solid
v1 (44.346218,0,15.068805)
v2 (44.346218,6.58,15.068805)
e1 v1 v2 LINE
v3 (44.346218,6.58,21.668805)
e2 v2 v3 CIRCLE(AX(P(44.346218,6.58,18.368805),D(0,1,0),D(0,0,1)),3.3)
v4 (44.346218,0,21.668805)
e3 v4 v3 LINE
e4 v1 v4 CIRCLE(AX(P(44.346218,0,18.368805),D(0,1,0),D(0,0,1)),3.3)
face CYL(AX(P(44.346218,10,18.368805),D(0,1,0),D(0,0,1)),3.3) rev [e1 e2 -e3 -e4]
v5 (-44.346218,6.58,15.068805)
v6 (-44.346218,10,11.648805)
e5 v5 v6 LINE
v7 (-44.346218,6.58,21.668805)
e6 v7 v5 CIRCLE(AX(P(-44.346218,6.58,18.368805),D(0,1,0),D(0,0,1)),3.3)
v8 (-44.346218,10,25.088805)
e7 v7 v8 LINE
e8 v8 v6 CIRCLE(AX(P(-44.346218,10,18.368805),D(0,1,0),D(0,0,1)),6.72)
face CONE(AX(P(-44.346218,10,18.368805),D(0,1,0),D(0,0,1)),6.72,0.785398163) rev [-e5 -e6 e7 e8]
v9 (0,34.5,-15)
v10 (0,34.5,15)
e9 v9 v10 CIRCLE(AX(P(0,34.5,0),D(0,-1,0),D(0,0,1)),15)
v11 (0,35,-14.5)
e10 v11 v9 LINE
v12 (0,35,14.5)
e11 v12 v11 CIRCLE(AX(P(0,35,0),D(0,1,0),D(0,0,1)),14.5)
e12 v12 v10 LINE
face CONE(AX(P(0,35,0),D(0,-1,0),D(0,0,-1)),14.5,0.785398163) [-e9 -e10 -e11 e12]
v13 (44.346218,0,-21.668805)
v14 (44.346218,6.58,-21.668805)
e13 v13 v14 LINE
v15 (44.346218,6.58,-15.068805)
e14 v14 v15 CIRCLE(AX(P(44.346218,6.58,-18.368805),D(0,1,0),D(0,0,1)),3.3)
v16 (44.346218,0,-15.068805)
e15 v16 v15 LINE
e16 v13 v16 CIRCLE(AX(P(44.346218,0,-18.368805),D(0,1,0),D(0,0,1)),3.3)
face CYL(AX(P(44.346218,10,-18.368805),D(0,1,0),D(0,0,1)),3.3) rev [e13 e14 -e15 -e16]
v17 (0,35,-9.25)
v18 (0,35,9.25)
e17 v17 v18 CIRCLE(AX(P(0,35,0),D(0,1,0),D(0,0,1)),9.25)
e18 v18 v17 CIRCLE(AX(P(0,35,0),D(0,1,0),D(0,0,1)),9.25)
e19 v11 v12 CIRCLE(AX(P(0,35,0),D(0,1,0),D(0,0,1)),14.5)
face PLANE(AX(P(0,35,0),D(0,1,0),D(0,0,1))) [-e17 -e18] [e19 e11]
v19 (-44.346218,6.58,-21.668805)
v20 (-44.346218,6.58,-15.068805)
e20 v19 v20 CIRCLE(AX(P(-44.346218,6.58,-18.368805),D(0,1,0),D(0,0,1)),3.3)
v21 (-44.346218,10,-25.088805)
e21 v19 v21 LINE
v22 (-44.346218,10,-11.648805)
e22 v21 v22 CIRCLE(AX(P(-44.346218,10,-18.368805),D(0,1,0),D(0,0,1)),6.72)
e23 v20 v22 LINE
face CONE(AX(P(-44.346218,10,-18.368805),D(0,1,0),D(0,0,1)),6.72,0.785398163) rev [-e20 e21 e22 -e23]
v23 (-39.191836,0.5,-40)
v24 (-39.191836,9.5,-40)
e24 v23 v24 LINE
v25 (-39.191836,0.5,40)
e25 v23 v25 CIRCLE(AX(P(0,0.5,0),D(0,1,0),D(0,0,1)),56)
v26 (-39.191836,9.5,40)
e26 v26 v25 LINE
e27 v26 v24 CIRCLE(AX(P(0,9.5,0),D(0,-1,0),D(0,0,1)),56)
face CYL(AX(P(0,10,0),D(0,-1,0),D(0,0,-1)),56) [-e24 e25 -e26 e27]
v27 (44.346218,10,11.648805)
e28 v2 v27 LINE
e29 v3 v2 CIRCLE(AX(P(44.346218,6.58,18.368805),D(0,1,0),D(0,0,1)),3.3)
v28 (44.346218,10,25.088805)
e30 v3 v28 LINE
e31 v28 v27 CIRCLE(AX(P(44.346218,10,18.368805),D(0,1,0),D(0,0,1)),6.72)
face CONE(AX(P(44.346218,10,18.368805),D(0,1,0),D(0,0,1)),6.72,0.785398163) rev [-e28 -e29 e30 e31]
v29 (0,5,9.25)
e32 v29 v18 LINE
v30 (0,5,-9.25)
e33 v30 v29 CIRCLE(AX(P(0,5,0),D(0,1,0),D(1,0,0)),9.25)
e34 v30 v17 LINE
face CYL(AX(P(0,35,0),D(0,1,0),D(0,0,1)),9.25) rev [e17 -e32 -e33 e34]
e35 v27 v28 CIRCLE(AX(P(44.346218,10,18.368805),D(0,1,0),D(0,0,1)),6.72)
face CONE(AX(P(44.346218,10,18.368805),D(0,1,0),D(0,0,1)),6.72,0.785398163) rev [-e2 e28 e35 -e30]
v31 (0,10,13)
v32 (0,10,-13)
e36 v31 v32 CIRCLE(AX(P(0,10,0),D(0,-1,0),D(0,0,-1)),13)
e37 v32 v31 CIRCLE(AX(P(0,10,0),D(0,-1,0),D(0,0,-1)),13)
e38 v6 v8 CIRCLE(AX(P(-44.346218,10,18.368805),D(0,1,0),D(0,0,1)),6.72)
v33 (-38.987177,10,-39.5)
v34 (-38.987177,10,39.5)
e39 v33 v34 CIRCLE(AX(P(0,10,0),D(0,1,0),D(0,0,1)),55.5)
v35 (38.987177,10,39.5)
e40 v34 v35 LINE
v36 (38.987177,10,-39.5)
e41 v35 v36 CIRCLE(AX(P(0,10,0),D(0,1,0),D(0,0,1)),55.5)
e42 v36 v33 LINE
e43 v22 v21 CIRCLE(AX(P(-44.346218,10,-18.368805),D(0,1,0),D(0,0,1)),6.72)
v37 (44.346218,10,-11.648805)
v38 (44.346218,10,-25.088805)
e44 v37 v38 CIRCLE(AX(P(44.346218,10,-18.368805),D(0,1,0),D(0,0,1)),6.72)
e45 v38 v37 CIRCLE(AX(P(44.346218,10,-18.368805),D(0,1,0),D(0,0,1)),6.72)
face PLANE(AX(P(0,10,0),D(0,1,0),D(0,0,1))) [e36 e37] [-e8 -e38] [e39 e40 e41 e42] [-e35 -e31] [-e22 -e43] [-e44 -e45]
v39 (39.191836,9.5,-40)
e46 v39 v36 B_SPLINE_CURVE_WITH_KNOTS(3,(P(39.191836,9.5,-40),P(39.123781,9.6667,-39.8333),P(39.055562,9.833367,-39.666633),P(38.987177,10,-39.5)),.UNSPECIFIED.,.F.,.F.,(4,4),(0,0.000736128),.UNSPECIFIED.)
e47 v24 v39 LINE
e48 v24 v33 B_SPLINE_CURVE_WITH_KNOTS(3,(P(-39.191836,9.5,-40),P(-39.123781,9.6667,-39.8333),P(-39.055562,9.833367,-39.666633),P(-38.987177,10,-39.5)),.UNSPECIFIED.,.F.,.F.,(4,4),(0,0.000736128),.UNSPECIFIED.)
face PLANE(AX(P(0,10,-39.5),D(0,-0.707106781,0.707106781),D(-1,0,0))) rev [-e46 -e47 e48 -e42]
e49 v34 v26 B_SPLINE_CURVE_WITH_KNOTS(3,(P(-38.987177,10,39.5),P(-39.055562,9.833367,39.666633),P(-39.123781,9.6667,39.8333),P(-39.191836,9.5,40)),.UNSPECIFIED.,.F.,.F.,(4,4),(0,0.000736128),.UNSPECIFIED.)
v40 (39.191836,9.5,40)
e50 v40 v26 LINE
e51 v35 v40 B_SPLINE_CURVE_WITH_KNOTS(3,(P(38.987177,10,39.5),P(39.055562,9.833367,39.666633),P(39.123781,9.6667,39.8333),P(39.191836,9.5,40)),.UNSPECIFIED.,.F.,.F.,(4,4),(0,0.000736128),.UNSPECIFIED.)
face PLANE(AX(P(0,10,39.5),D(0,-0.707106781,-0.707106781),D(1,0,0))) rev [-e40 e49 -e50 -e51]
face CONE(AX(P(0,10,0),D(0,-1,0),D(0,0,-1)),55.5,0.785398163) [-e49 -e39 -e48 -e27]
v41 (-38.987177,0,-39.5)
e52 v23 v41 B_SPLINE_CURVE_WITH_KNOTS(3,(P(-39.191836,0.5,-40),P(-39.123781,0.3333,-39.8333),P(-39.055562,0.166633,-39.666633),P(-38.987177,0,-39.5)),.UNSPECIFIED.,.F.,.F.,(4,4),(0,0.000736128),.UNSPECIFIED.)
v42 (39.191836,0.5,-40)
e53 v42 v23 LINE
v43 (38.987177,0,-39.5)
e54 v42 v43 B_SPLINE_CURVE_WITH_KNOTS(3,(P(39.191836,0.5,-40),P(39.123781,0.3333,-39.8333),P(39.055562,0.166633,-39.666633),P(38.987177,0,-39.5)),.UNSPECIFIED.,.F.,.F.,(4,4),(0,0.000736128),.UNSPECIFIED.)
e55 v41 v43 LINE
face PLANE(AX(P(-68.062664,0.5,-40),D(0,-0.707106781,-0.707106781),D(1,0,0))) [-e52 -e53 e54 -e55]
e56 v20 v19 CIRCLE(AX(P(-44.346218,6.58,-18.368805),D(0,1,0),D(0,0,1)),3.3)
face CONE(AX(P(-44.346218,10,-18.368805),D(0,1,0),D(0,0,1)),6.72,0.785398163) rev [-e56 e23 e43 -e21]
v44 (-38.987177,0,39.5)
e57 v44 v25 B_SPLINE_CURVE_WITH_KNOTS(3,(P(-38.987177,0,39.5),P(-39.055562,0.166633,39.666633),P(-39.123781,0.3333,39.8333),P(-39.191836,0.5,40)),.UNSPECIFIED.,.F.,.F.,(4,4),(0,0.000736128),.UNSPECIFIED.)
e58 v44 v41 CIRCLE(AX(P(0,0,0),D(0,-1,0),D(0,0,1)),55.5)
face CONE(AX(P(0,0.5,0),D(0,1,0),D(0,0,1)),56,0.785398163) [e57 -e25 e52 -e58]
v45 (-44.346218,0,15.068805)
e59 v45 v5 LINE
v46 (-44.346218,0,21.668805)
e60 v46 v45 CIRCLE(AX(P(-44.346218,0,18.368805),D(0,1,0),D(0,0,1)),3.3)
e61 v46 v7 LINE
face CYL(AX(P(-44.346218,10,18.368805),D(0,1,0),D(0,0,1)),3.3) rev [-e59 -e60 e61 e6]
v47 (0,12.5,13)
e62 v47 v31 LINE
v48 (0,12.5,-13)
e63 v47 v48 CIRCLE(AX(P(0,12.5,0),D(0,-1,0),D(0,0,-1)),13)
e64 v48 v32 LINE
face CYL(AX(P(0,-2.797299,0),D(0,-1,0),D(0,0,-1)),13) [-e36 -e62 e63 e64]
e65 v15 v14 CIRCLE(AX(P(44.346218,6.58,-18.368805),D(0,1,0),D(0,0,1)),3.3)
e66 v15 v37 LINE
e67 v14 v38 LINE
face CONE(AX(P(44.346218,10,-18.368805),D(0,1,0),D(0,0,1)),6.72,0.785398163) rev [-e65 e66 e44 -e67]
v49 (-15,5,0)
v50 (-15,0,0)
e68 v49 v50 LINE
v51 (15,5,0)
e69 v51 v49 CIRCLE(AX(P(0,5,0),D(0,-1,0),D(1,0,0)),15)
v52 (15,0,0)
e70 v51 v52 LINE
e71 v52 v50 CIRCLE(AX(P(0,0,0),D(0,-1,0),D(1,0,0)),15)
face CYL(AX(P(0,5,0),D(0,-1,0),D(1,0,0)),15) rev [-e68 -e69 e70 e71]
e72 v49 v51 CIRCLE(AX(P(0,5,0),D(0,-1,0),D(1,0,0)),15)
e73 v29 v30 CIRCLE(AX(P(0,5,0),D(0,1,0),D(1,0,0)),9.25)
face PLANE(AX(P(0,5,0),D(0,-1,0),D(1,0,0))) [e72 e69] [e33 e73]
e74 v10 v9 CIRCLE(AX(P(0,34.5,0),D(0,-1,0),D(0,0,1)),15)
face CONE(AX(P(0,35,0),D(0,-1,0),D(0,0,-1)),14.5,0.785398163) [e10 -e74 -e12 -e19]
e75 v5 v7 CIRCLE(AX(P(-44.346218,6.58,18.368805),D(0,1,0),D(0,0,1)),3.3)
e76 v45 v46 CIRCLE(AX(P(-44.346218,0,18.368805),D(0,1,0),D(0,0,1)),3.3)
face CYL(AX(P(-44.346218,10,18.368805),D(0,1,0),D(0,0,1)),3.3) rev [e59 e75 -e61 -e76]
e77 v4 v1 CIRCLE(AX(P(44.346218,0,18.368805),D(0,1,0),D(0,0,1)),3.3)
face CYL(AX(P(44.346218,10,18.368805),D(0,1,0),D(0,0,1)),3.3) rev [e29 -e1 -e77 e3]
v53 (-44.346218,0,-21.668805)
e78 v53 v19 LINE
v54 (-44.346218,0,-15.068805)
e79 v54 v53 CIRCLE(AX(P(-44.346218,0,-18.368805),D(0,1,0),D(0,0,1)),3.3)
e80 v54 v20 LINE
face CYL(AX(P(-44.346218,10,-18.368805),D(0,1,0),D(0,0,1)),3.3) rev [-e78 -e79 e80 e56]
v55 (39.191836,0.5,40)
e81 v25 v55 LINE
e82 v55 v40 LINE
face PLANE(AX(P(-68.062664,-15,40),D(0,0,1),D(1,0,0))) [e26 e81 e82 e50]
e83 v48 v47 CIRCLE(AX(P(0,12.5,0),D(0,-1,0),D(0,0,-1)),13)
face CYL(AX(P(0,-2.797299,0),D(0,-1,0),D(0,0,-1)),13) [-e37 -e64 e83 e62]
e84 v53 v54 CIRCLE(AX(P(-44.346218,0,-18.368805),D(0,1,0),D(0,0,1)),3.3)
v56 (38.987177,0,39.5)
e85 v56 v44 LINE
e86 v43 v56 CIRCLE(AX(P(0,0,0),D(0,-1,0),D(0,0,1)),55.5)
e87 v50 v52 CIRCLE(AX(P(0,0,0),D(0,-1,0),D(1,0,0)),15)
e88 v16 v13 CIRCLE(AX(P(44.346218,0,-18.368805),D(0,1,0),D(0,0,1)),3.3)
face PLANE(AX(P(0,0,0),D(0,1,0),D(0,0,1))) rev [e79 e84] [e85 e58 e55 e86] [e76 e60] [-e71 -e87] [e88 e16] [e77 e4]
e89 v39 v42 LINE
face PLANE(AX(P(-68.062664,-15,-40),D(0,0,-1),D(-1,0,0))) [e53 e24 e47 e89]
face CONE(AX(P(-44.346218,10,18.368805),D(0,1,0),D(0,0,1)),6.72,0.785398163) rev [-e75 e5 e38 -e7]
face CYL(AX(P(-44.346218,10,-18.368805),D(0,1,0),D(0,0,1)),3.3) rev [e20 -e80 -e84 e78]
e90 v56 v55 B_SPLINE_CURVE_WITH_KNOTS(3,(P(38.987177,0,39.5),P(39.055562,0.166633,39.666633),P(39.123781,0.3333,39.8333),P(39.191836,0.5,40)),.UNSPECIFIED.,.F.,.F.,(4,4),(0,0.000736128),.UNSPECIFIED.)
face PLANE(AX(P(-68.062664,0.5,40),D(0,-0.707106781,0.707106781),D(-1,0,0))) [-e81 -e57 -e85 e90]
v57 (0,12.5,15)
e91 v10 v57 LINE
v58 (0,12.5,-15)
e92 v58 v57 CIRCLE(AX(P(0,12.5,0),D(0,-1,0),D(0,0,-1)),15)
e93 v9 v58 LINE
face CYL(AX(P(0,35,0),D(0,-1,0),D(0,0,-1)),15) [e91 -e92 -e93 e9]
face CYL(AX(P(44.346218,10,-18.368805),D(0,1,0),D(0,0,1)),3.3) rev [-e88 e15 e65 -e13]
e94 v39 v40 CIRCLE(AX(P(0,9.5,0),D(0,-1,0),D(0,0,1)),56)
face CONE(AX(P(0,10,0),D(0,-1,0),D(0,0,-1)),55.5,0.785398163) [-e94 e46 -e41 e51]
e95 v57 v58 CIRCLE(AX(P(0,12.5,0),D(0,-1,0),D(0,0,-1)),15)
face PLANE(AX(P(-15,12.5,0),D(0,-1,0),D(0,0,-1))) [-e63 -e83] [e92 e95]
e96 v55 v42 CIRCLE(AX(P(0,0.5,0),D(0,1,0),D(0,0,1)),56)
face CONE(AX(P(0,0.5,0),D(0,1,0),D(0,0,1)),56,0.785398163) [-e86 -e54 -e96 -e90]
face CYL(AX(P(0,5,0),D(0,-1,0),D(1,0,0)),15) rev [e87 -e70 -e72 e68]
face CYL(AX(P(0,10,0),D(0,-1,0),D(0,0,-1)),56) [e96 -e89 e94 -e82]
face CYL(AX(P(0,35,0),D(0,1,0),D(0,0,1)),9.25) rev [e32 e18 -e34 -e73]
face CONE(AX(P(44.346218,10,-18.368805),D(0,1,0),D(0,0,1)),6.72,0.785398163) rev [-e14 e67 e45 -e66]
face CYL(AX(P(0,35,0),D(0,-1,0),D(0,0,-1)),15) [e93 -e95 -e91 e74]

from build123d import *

# Parameters (mm, degrees)
SKETCH_1_R                   = 56
EXTRUDE_1_DEPTH              = 10
SKETCH_2_R                   = 15
EXTRUDE_2_DEPTH              = 25
M20X1_5_1_D                  = 18.5
M20X1_5_1_DEPTH              = 44.5
M20X1_5_1_TIP                = 5.557960726
HOLE_WIZARD_M6_1_D           = 6.6
HOLE_WIZARD_M6_1_CSINK_D     = 13.44
HOLE_WIZARD_M6_1_CSINK_ANGLE = 90
SKETCH_12_OUTSIDE_W          = 146.442
SKETCH_12_OUTSIDE_H          = 146.442
SKETCH_12_OUTSIDE_W_2        = 136.125327254
SKETCH_12_OUTSIDE_H_2        = 80
CUT_EXTRUDE_1_DEPTH          = 25
SKETCH_13_W                  = 2
SKETCH_13_H                  = 2.5
CHAMFER_7_SIZE               = 0.5
SKETCH_14_R                  = 15
CUT_EXTRUDE_2_DEPTH          = 5


with BuildPart() as part:
    # 草图1 → 凸台-拉伸1 (new body)
    with BuildSketch(Plane(origin=(0, 0, 0), x_dir=(1, 0, 0), z_dir=(0, 1, 0))):
        with Locations(Location((0, 0, 0), (0, 0, 270))):
            Circle(SKETCH_1_R)
    extrude(amount=EXTRUDE_1_DEPTH)

    # 草图2 → 凸台-拉伸2 (add)
    with BuildSketch(Plane(origin=(0, 10, 0), x_dir=(1, 0, 0), z_dir=(0, 1, 0))):
        with Locations(Location((0, 0, 0), (0, 0, 270))):
            Circle(SKETCH_2_R)
    extrude(amount=EXTRUDE_2_DEPTH)

    # M20x1.5 螺纹孔1
    with Locations(Plane(origin=(0, 35, 0), x_dir=(1, 0, 0), z_dir=(0, 1, 0))):
        with Locations((0, 0)):
            Hole(M20X1_5_1_D / 2, depth=M20X1_5_1_DEPTH)
            with Locations((0, 0, -(M20X1_5_1_DEPTH + M20X1_5_1_TIP / 2))):  # 118° drill point
                Cone(0, M20X1_5_1_D / 2, M20X1_5_1_TIP, mode=Mode.SUBTRACT)

    # M6 六角凹锥坑螺钉的锥形沉头孔1 (through all)
    with Locations(Plane(origin=(0, 10, 0), x_dir=(1, 0, 0), z_dir=(0, 1, 0))):
        with Locations((44.346217561, -18.368804754), (-44.346217561, 18.368804754), (-44.346217561, -18.368804754), (44.346217561, 18.368804754)):
            CounterSinkHole(HOLE_WIZARD_M6_1_D / 2, HOLE_WIZARD_M6_1_CSINK_D / 2, counter_sink_angle=HOLE_WIZARD_M6_1_CSINK_ANGLE)

    # 草图12 outside → 切除-拉伸1 (cut)
    with BuildSketch(Plane(origin=(0, 10, 0), x_dir=(1, 0, 0), z_dir=(0, 1, 0))):
        Rectangle(SKETCH_12_OUTSIDE_W, SKETCH_12_OUTSIDE_H)
        Rectangle(SKETCH_12_OUTSIDE_W_2, SKETCH_12_OUTSIDE_H_2, mode=Mode.SUBTRACT)
    extrude(amount=-CUT_EXTRUDE_1_DEPTH, mode=Mode.SUBTRACT)

    # 草图13 → 切除-旋转1 (revolve, cut)
    with BuildSketch(Plane.XY, mode=Mode.PRIVATE) as cut_revolve_1_sk:
        with Locations((-14, 11.25)):
            Rectangle(SKETCH_13_W, SKETCH_13_H)
    revolve(cut_revolve_1_sk.sketch.rotate(Axis((0, -2.79729943, 0), (0, 1, 0)), 270), axis=Axis((0, -2.79729943, 0), (0, 1, 0)), mode=Mode.SUBTRACT)

    # 倒角7
    chamfer_7_edges = [part.edges().sort_by_distance(p)[0] for p in [
        (56, 0, 0),
        (56, 10, 0),
        (-56, 0, 0),
        (0, 0, -40),
        (0, 0, 40),
        (-56, 10, 0),
        (0, 10, 40),
        (0, 10, -40),
        (0, 35, -15),
    ]]
    chamfer(chamfer_7_edges, length=CHAMFER_7_SIZE)

    # 草图14 → 切除-拉伸2 (cut)
    with BuildSketch(Plane.XZ):
        with Locations(Location((0, 0, 0), (0, 0, 270))):
            Circle(SKETCH_14_R)
    extrude(amount=-CUT_EXTRUDE_2_DEPTH, mode=Mode.SUBTRACT)


solid = part.part
